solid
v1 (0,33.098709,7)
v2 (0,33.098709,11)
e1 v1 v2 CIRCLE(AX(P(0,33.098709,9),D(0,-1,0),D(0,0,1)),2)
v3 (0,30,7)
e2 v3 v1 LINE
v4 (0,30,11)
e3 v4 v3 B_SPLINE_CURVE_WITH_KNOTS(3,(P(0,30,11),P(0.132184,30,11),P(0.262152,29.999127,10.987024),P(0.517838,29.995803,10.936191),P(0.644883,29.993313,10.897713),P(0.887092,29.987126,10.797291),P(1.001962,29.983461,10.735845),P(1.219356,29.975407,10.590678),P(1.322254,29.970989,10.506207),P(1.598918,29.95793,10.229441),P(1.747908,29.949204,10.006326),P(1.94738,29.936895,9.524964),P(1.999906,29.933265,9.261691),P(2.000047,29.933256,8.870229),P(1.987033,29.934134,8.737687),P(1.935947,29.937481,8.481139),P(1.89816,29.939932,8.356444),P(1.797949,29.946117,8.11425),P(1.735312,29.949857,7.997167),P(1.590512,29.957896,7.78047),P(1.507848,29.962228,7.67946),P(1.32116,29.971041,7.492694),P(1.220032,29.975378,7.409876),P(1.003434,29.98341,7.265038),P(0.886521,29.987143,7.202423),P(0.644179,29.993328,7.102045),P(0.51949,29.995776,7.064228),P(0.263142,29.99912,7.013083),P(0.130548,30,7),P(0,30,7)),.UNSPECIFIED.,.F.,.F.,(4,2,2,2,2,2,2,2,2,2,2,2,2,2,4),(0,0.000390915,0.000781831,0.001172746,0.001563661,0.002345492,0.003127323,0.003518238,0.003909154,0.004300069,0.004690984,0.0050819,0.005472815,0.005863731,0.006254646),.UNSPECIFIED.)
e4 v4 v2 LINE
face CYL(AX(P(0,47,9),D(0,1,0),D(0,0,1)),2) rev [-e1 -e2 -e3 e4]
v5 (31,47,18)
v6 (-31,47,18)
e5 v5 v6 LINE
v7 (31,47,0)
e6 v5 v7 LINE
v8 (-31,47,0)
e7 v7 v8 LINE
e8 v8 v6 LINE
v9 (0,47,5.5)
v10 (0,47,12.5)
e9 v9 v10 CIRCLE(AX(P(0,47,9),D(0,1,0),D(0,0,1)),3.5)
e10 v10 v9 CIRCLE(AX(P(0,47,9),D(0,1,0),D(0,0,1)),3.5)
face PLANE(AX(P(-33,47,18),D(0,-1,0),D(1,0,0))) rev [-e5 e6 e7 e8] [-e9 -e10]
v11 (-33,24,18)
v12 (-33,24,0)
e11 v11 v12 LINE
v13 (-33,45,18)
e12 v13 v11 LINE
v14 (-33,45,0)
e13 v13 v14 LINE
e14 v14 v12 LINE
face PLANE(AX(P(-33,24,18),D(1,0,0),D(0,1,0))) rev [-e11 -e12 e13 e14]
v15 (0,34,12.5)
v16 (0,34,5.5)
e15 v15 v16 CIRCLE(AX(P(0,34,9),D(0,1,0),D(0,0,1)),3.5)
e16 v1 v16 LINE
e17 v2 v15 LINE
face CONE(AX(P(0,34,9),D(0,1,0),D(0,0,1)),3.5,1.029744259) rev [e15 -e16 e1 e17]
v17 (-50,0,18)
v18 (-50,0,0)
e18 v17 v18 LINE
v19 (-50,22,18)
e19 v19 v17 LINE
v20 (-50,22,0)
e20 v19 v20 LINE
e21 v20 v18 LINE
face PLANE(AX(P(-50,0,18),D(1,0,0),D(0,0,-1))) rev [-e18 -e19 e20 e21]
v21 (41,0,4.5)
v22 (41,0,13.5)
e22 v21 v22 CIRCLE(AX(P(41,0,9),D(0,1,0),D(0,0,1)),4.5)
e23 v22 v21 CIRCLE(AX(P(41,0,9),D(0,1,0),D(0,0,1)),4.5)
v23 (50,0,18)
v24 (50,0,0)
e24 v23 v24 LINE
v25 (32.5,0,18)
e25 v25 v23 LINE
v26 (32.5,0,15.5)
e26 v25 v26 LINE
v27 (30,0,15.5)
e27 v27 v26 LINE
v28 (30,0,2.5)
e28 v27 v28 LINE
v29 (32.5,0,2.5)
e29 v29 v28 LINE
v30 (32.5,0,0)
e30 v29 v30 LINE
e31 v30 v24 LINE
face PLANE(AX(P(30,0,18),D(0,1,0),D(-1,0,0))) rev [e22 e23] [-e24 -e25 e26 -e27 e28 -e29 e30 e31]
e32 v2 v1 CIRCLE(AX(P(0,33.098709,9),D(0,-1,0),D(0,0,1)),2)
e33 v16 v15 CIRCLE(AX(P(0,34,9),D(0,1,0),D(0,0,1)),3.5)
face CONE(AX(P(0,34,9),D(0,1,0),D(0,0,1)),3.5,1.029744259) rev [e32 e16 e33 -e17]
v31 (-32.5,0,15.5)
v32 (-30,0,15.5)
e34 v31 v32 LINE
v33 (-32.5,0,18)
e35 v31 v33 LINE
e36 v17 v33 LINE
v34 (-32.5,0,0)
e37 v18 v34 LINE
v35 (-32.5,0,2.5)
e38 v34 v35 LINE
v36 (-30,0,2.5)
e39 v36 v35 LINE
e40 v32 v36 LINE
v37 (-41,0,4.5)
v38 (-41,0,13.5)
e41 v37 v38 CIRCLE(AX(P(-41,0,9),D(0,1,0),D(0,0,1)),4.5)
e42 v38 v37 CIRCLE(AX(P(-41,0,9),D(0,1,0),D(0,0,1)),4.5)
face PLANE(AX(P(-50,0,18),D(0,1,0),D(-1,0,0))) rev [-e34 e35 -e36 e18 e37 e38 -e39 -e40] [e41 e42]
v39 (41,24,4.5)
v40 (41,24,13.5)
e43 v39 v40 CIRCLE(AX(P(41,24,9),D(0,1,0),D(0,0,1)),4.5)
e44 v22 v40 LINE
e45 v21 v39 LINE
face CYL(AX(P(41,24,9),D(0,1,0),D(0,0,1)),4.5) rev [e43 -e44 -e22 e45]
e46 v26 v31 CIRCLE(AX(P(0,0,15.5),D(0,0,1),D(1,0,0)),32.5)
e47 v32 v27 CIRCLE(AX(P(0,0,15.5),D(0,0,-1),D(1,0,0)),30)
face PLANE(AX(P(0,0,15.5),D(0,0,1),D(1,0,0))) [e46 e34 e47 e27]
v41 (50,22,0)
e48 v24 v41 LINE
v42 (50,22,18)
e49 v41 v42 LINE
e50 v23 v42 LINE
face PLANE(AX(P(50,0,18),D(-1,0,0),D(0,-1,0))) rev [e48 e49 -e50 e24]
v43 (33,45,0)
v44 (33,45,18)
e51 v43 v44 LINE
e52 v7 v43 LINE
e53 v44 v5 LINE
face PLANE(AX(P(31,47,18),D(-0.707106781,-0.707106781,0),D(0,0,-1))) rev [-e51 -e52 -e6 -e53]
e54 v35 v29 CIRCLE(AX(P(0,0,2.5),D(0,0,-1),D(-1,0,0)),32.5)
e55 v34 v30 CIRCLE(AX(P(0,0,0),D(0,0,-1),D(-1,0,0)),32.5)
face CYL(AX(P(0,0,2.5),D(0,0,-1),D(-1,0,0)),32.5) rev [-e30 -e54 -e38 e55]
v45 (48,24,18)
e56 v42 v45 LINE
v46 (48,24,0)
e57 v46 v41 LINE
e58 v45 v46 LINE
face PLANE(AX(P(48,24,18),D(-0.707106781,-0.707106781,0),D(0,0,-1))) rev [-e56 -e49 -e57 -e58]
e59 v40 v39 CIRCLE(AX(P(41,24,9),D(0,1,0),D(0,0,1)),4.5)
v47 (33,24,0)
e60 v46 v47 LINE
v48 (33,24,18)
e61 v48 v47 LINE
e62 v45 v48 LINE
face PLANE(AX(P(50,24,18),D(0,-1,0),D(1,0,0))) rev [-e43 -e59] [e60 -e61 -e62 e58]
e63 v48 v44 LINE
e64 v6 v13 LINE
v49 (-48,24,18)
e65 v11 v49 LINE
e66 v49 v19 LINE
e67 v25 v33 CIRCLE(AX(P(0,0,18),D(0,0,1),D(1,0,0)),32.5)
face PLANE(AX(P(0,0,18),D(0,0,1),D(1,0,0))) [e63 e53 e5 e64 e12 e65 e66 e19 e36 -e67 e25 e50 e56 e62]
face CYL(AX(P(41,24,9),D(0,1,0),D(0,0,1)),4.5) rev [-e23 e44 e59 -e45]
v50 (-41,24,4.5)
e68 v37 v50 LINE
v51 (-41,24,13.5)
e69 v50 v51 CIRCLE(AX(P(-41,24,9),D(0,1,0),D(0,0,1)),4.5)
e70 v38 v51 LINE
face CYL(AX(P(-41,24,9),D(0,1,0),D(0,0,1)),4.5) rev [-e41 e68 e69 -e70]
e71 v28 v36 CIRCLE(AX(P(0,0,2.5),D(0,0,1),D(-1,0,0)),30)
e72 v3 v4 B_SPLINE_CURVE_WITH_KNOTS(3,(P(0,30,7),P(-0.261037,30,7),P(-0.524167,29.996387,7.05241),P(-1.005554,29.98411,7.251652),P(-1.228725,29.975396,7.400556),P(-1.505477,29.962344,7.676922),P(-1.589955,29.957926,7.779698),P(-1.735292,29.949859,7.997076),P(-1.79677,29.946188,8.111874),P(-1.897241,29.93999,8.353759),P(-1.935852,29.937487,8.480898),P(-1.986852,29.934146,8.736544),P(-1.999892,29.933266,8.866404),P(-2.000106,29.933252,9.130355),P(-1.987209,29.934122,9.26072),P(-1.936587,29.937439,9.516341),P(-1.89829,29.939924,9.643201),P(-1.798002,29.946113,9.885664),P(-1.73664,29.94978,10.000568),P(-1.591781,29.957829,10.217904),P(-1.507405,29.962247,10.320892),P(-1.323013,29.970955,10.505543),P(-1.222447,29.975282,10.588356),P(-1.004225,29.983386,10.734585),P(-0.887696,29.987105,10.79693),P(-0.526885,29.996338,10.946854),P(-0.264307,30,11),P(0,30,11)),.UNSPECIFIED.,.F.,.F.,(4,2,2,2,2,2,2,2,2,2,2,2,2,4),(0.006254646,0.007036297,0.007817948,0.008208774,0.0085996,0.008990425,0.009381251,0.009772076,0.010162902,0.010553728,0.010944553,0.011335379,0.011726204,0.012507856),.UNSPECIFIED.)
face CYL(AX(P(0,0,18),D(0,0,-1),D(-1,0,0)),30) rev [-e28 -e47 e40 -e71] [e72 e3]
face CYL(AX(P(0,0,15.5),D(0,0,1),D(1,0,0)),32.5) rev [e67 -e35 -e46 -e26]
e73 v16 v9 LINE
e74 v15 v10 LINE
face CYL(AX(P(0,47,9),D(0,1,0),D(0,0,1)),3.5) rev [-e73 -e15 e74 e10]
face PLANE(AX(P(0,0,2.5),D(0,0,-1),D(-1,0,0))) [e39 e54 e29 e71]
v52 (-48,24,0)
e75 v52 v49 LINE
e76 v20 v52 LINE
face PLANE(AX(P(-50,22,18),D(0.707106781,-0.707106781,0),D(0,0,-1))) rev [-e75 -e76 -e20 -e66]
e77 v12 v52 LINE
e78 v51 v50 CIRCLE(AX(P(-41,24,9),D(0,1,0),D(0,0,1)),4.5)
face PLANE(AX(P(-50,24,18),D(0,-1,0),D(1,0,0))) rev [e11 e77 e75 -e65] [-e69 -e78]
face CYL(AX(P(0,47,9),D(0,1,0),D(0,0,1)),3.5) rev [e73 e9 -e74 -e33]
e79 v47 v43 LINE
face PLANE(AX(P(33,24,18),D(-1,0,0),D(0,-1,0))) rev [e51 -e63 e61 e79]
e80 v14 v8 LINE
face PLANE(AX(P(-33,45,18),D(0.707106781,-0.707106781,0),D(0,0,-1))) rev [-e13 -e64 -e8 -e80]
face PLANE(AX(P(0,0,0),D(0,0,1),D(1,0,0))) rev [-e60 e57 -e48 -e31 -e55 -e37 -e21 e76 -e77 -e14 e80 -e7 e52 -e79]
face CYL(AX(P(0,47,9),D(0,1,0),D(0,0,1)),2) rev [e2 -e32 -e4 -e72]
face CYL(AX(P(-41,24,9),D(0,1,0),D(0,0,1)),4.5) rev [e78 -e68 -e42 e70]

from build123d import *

# Parameters (mm, degrees)
BOSS_EXTRUDE1_DEPTH       = 18
CHAMFER1_SIZE             = 2
M8X1_0_TAPPED_HOLE1_D     = 7
M8X1_0_TAPPED_HOLE1_DEPTH = 13
M8X1_0_TAPPED_HOLE1_TIP   = 2.103012167
HOLE2_D                   = 9
SKETCH15_R                = 32.5
CUT_EXTRUDE3_DEPTH        = 2.5
CUT_EXTRUDE4_START        = -2.5
SKETCH16_R                = 32.5
CUT_EXTRUDE4_DEPTH        = 2.5
HOLE3_D                   = 4


with BuildPart() as part:
    # Sketch1 → Boss-Extrude1 (new body)
    with BuildSketch(Plane.XY):
        with BuildLine():
            Line((-50, 24), (-33, 24))
            Line((-33, 24), (-33, 47))
            Line((-33, 47), (33, 47))
            Line((33, 47), (33, 24))
            Line((33, 24), (50, 24))
            Line((50, 24), (50, 0))
            Line((50, 0), (30, 0))
            ThreePointArc((30, 0), (0, 30), (-30, 0))
            Line((-30, 0), (-50, 0))
            Line((-50, 0), (-50, 24))
        make_face()
    extrude(amount=BOSS_EXTRUDE1_DEPTH)

    # Chamfer1
    chamfer1_edges = [part.edges().sort_by_distance(p)[0] for p in [
        (-50, 24, 9),
        (-33, 47, 9),
        (33, 47, 9),
        (50, 24, 9),
    ]]
    chamfer(chamfer1_edges, length=CHAMFER1_SIZE)

    # M8x1.0 Tapped Hole1
    with Locations(Plane(origin=(0, 47, 0), x_dir=(1, 0, 0), z_dir=(0, 1, 0))):
        with Locations((0, -9)):
            Hole(M8X1_0_TAPPED_HOLE1_D / 2, depth=M8X1_0_TAPPED_HOLE1_DEPTH)
            with Locations((0, 0, -(M8X1_0_TAPPED_HOLE1_DEPTH + M8X1_0_TAPPED_HOLE1_TIP / 2))):  # 118° drill point
                Cone(0, M8X1_0_TAPPED_HOLE1_D / 2, M8X1_0_TAPPED_HOLE1_TIP, mode=Mode.SUBTRACT)

    # Hole2 (through all)
    with Locations(Plane(origin=(0, 24, 0), x_dir=(1, 0, 0), z_dir=(0, 1, 0))):
        with Locations((-41, -9), (41, -9)):
            Hole(HOLE2_D / 2)

    # Sketch15 → Cut-Extrude3 (cut)
    with BuildSketch(Plane(origin=(0, 0, 0), x_dir=(-1, 0, 0), z_dir=(0, 0, -1))):
        Circle(SKETCH15_R)
    extrude(amount=-CUT_EXTRUDE3_DEPTH, mode=Mode.SUBTRACT)

    # Sketch16 → Cut-Extrude4 (cut)
    with BuildSketch(Plane.XY.offset(18).offset(CUT_EXTRUDE4_START)):
        Circle(SKETCH16_R)
    extrude(amount=CUT_EXTRUDE4_DEPTH, mode=Mode.SUBTRACT)

    # Hole3 (through all)
    with Locations(Plane(origin=(0, 47, 0), x_dir=(1, 0, 0), z_dir=(0, 1, 0))):
        with Locations((0, -9)):
            Hole(HOLE3_D / 2)


solid = part.part
